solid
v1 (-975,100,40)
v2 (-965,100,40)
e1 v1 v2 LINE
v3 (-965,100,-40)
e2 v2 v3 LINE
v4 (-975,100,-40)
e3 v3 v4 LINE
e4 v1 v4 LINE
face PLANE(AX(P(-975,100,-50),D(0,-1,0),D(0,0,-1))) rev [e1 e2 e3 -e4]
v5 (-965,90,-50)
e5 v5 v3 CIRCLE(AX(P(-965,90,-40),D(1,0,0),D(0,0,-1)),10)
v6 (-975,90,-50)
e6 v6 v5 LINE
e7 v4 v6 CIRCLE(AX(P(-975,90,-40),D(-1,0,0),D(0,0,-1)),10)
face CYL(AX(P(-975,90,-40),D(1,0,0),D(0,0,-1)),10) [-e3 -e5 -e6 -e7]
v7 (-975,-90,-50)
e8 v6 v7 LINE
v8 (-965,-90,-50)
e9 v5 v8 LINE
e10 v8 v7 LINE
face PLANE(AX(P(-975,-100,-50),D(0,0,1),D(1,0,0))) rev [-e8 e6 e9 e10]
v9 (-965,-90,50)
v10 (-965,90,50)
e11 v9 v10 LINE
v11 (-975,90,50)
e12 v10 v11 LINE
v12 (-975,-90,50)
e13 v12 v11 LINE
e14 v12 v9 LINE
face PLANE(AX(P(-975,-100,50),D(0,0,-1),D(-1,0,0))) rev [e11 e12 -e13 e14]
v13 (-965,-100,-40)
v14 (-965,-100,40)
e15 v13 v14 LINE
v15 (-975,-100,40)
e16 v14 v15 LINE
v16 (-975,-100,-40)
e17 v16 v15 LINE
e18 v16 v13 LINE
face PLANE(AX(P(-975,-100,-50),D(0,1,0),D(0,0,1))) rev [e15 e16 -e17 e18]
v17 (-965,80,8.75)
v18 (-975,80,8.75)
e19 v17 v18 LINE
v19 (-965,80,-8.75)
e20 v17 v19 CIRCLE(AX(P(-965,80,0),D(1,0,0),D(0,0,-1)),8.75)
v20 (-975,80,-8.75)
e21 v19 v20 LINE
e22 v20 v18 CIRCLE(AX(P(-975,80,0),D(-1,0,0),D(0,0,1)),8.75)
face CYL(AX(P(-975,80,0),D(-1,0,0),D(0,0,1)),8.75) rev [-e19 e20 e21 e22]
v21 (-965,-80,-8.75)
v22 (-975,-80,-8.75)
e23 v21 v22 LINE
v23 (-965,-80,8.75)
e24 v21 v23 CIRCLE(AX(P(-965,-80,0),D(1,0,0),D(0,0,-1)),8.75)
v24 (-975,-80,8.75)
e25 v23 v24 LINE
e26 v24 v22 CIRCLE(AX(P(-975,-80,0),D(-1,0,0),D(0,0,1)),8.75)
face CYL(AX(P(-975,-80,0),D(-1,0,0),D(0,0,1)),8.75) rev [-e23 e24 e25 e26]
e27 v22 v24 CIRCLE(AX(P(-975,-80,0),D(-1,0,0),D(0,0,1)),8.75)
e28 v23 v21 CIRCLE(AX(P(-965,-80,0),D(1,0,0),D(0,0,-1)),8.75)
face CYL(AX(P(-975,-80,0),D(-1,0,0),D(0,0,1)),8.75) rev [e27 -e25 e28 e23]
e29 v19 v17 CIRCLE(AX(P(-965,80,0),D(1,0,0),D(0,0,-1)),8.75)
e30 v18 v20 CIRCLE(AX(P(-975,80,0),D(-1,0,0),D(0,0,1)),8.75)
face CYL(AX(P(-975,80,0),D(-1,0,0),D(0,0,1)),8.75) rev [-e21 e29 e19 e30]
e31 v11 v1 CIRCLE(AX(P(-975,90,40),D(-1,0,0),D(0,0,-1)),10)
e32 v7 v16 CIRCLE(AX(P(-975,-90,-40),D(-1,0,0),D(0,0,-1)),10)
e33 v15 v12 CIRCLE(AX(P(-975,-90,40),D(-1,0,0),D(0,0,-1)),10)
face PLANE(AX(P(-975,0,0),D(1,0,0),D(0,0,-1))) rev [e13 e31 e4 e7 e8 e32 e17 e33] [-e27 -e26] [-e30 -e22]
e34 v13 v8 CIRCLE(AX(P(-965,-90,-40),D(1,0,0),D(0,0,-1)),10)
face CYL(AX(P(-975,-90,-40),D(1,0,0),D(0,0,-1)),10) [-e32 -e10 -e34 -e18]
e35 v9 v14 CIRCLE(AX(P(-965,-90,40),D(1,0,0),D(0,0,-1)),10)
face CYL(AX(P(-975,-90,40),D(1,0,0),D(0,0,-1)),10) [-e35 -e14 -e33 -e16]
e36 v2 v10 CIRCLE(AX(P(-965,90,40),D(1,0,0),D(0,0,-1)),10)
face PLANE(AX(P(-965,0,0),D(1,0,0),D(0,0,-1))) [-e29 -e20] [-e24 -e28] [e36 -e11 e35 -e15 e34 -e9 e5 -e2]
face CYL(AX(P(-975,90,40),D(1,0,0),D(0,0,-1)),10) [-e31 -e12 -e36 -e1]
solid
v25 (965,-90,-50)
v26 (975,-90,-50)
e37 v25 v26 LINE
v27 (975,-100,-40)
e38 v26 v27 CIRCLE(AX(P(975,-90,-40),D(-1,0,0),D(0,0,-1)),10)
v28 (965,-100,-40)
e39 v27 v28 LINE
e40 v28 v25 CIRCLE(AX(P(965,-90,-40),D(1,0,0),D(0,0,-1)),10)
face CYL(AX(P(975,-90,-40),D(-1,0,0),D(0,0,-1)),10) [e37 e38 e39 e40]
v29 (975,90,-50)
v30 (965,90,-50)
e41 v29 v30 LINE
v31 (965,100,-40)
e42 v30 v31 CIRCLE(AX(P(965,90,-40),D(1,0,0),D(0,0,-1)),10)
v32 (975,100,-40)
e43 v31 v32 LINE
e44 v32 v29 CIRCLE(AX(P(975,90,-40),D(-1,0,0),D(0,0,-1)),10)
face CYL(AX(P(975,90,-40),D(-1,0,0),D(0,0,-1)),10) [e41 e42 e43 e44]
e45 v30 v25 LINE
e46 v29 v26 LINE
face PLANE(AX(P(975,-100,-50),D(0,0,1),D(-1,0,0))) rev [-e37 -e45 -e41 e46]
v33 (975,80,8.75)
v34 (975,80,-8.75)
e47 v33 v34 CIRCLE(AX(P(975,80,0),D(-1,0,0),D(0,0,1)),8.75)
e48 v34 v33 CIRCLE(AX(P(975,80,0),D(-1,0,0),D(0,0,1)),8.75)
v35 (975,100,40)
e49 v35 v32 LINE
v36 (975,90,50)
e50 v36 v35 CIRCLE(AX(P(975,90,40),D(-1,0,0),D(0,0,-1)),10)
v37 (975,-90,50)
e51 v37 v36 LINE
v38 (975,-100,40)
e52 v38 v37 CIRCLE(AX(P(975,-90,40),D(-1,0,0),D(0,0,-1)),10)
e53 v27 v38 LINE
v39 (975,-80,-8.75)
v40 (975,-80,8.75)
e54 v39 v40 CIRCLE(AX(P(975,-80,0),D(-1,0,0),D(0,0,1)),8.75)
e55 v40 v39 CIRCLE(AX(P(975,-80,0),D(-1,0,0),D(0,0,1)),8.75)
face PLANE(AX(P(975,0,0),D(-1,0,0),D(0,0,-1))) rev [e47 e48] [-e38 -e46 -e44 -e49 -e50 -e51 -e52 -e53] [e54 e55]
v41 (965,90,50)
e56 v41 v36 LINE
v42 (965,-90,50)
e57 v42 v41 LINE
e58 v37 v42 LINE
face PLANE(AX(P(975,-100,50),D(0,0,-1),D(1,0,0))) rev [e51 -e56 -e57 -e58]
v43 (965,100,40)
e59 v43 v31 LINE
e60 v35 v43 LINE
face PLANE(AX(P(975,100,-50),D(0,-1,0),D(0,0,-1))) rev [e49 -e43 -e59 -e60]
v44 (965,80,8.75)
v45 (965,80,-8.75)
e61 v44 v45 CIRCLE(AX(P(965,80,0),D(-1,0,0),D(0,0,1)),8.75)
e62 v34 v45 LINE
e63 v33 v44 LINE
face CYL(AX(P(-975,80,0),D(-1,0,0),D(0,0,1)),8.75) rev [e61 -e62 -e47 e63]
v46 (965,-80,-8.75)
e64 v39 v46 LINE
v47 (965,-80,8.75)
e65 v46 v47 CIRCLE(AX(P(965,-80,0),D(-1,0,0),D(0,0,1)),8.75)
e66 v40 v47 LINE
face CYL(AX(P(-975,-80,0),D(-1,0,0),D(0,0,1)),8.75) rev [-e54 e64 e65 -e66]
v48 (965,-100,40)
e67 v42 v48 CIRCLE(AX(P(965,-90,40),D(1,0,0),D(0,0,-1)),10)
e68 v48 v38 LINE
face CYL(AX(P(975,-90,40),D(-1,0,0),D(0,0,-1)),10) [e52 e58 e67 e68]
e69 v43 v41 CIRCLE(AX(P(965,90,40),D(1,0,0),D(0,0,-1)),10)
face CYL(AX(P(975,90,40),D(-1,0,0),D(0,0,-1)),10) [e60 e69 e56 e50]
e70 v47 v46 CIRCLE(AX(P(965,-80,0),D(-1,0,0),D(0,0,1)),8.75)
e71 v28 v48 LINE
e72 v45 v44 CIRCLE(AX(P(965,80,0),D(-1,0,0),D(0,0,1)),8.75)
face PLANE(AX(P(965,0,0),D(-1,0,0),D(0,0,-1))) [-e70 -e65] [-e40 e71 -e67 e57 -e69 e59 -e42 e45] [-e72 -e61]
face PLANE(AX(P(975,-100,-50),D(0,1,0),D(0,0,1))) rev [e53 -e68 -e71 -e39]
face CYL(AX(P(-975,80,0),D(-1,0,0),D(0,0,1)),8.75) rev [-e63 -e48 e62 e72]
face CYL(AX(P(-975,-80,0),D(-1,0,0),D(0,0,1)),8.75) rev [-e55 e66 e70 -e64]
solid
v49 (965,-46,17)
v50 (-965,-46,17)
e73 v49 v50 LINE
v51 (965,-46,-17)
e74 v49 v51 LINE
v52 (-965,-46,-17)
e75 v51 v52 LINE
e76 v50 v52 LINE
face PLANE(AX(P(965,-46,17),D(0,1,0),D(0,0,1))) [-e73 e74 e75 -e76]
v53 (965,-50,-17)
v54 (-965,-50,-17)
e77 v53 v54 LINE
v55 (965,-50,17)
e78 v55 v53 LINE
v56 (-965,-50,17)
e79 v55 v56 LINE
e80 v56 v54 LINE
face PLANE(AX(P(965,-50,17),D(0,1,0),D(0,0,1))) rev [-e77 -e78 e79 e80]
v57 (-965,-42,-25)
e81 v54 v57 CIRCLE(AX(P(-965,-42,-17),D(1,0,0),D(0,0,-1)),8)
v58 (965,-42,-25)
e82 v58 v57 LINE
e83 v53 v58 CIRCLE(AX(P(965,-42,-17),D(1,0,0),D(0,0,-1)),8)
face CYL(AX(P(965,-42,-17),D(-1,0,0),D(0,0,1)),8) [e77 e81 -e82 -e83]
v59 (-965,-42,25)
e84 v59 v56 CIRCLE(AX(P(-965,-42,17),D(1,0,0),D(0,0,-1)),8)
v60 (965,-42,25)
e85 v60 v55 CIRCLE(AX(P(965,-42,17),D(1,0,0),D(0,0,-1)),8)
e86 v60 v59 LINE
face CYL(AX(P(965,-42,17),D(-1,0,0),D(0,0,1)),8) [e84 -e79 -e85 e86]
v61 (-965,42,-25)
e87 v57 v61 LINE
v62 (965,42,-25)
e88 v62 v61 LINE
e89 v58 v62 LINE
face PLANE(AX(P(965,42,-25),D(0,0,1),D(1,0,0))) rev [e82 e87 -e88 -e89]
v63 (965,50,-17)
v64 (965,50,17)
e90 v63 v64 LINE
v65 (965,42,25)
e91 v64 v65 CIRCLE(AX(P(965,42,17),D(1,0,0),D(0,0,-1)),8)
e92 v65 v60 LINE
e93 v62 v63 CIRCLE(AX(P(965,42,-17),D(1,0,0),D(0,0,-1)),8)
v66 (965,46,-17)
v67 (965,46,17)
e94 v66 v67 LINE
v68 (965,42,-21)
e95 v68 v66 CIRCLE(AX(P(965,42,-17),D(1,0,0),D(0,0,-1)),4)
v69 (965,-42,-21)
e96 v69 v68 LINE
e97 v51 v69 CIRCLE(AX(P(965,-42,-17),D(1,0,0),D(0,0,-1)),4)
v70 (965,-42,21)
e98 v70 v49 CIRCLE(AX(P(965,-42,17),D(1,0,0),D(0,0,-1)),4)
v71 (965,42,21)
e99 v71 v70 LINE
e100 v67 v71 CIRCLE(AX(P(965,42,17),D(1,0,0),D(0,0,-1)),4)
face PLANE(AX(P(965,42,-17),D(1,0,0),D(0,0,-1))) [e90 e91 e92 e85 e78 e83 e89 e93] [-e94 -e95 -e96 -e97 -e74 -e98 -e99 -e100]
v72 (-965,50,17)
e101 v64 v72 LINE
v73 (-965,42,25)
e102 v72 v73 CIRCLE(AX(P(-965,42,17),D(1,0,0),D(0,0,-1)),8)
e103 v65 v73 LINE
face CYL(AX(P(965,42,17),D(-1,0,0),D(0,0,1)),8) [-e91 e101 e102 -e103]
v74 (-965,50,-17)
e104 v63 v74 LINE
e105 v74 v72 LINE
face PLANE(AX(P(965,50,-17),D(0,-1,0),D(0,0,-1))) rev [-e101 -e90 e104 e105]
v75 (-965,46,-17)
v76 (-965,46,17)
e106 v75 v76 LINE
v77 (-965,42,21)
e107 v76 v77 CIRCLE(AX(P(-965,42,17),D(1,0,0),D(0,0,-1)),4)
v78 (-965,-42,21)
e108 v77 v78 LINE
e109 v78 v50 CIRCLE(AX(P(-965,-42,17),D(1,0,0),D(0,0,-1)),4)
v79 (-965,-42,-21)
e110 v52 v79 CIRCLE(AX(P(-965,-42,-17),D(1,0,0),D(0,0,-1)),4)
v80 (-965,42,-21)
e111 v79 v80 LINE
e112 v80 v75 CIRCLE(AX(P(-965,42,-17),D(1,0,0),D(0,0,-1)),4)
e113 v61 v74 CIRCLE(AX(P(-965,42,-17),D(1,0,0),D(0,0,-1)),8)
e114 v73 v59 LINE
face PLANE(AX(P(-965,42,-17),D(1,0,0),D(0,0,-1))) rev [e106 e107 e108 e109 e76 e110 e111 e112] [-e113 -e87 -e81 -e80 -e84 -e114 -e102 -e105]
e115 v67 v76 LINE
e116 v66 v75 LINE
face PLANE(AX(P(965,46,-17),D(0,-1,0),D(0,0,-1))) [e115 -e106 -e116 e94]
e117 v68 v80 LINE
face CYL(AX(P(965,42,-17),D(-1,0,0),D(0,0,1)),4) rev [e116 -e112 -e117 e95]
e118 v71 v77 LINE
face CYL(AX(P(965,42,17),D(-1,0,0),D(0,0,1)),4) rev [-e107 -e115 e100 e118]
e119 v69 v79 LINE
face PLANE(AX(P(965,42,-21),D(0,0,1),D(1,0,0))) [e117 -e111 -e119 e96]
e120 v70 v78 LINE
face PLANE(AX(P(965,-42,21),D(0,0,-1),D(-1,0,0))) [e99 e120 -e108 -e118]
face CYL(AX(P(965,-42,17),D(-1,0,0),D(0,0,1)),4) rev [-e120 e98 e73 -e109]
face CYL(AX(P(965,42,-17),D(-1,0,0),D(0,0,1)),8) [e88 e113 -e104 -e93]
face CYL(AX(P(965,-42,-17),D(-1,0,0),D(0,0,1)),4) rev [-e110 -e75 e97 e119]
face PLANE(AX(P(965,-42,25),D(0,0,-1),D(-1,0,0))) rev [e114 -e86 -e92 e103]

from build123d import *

# Parameters (mm, degrees)
GB_6728_1986_RECTANGULAR_HOLLOW_SECTION_DEPTH = 1930
SKETCH4_W                                     = 100
SKETCH4_H                                     = 200
BOSS_EXTRUDE1_DEPTH                           = 10
FILLET1_R                                     = 10
SKETCH9_W                                     = 8.75
SKETCH9_H                                     = 1950
M16_CLEARANCE_HOLE2_AT_2_COUNT                = 2
M16_CLEARANCE_HOLE2_AT_2_PITCH                = 160


with BuildPart() as part:
    # Sketch1 → Gb／6728-1986 rectangular hollow section 100 X 50 X 4 (1) (new body)
    with BuildSketch(Plane(origin=(-965, 0, 0), x_dir=(0, 0, -1), z_dir=(1, 0, 0))):
        with BuildLine():
            Line((-17, -50), (17, -50))
            ThreePointArc((17, -50), (22.656854249, -47.656854249), (25, -42))
            Line((25, -42), (25, 42))
            ThreePointArc((25, 42), (22.656854249, 47.656854249), (17, 50))
            Line((17, 50), (-17, 50))
            ThreePointArc((-17, 50), (-22.656854249, 47.656854249), (-25, 42))
            Line((-25, 42), (-25, -42))
            ThreePointArc((-25, -42), (-22.656854249, -47.656854249), (-17, -50))
        make_face()
        with BuildLine():
            Line((-17, -46), (17, -46))
            ThreePointArc((17, -46), (19.828427125, -44.828427125), (21, -42))
            Line((21, -42), (21, 42))
            ThreePointArc((21, 42), (19.828427125, 44.828427125), (17, 46))
            Line((17, 46), (-17, 46))
            ThreePointArc((-17, 46), (-19.828427125, 44.828427125), (-21, 42))
            Line((-21, 42), (-21, -42))
            ThreePointArc((-21, -42), (-19.828427125, -44.828427125), (-17, -46))
        make_face(mode=Mode.SUBTRACT)
    extrude(amount=GB_6728_1986_RECTANGULAR_HOLLOW_SECTION_DEPTH)


with BuildPart() as body_2:
    # Sketch4 → Boss-Extrude1 (new body)
    with BuildSketch(Plane.ZY.offset(965)):
        Rectangle(SKETCH4_W, SKETCH4_H)
    extrude(amount=BOSS_EXTRUDE1_DEPTH)

    # Fillet1
    fillet1_edges = [body_2.edges().sort_by_distance(p)[0] for p in [
        (-970, -100, 50),
        (-970, -100, -50),
        (-970, 100, -50),
        (-970, 100, 50),
    ]]
    fillet(fillet1_edges, radius=FILLET1_R)


with BuildPart() as body_3:
    # Mirror2: mirrored copy
    add(body_2.part.mirror(Plane.ZY))


with BuildPart() as m16_clearance_hole2_tool:
    # Sketch9 → M16 Clearance Hole2 (revolve)
    with BuildSketch(Plane(origin=(-975, 80, 0), x_dir=(0, 0, 1), z_dir=(0, 1, 0))):
        with Locations((4.375, 975)):
            Rectangle(SKETCH9_W, SKETCH9_H)
    m16_clearance_hole2 = revolve(axis=Axis((-981.35, 80, 0), (1, 0, 0)))


with BuildPart() as body_2_1:
    add(body_2.part)

    # M16 Clearance Hole2: cut by m16_clearance_hole2_tool
    add(m16_clearance_hole2_tool.part, mode=Mode.SUBTRACT)


with BuildPart() as body_3_1:
    add(body_3.part)

    # M16 Clearance Hole2: cut by m16_clearance_hole2_tool
    add(m16_clearance_hole2_tool.part, mode=Mode.SUBTRACT)


with BuildPart() as m16_clearance_hole2_at_2_tool:
    # M16 Clearance Hole2 at 2: M16 Clearance Hole2 ×2
    with Locations(*[(0, -i * M16_CLEARANCE_HOLE2_AT_2_PITCH, 0) for i in range(1, M16_CLEARANCE_HOLE2_AT_2_COUNT)]):
        add(m16_clearance_hole2)


with BuildPart() as body_2_2:
    add(body_2_1.part)

    # M16 Clearance Hole2 at 2: cut by m16_clearance_hole2_at_2_tool
    add(m16_clearance_hole2_at_2_tool.part, mode=Mode.SUBTRACT)


with BuildPart() as body_3_2:
    add(body_3_1.part)

    # M16 Clearance Hole2 at 2: cut by m16_clearance_hole2_at_2_tool
    add(m16_clearance_hole2_at_2_tool.part, mode=Mode.SUBTRACT)


solid = Compound([part.part, body_2_2.part, body_3_2.part])
